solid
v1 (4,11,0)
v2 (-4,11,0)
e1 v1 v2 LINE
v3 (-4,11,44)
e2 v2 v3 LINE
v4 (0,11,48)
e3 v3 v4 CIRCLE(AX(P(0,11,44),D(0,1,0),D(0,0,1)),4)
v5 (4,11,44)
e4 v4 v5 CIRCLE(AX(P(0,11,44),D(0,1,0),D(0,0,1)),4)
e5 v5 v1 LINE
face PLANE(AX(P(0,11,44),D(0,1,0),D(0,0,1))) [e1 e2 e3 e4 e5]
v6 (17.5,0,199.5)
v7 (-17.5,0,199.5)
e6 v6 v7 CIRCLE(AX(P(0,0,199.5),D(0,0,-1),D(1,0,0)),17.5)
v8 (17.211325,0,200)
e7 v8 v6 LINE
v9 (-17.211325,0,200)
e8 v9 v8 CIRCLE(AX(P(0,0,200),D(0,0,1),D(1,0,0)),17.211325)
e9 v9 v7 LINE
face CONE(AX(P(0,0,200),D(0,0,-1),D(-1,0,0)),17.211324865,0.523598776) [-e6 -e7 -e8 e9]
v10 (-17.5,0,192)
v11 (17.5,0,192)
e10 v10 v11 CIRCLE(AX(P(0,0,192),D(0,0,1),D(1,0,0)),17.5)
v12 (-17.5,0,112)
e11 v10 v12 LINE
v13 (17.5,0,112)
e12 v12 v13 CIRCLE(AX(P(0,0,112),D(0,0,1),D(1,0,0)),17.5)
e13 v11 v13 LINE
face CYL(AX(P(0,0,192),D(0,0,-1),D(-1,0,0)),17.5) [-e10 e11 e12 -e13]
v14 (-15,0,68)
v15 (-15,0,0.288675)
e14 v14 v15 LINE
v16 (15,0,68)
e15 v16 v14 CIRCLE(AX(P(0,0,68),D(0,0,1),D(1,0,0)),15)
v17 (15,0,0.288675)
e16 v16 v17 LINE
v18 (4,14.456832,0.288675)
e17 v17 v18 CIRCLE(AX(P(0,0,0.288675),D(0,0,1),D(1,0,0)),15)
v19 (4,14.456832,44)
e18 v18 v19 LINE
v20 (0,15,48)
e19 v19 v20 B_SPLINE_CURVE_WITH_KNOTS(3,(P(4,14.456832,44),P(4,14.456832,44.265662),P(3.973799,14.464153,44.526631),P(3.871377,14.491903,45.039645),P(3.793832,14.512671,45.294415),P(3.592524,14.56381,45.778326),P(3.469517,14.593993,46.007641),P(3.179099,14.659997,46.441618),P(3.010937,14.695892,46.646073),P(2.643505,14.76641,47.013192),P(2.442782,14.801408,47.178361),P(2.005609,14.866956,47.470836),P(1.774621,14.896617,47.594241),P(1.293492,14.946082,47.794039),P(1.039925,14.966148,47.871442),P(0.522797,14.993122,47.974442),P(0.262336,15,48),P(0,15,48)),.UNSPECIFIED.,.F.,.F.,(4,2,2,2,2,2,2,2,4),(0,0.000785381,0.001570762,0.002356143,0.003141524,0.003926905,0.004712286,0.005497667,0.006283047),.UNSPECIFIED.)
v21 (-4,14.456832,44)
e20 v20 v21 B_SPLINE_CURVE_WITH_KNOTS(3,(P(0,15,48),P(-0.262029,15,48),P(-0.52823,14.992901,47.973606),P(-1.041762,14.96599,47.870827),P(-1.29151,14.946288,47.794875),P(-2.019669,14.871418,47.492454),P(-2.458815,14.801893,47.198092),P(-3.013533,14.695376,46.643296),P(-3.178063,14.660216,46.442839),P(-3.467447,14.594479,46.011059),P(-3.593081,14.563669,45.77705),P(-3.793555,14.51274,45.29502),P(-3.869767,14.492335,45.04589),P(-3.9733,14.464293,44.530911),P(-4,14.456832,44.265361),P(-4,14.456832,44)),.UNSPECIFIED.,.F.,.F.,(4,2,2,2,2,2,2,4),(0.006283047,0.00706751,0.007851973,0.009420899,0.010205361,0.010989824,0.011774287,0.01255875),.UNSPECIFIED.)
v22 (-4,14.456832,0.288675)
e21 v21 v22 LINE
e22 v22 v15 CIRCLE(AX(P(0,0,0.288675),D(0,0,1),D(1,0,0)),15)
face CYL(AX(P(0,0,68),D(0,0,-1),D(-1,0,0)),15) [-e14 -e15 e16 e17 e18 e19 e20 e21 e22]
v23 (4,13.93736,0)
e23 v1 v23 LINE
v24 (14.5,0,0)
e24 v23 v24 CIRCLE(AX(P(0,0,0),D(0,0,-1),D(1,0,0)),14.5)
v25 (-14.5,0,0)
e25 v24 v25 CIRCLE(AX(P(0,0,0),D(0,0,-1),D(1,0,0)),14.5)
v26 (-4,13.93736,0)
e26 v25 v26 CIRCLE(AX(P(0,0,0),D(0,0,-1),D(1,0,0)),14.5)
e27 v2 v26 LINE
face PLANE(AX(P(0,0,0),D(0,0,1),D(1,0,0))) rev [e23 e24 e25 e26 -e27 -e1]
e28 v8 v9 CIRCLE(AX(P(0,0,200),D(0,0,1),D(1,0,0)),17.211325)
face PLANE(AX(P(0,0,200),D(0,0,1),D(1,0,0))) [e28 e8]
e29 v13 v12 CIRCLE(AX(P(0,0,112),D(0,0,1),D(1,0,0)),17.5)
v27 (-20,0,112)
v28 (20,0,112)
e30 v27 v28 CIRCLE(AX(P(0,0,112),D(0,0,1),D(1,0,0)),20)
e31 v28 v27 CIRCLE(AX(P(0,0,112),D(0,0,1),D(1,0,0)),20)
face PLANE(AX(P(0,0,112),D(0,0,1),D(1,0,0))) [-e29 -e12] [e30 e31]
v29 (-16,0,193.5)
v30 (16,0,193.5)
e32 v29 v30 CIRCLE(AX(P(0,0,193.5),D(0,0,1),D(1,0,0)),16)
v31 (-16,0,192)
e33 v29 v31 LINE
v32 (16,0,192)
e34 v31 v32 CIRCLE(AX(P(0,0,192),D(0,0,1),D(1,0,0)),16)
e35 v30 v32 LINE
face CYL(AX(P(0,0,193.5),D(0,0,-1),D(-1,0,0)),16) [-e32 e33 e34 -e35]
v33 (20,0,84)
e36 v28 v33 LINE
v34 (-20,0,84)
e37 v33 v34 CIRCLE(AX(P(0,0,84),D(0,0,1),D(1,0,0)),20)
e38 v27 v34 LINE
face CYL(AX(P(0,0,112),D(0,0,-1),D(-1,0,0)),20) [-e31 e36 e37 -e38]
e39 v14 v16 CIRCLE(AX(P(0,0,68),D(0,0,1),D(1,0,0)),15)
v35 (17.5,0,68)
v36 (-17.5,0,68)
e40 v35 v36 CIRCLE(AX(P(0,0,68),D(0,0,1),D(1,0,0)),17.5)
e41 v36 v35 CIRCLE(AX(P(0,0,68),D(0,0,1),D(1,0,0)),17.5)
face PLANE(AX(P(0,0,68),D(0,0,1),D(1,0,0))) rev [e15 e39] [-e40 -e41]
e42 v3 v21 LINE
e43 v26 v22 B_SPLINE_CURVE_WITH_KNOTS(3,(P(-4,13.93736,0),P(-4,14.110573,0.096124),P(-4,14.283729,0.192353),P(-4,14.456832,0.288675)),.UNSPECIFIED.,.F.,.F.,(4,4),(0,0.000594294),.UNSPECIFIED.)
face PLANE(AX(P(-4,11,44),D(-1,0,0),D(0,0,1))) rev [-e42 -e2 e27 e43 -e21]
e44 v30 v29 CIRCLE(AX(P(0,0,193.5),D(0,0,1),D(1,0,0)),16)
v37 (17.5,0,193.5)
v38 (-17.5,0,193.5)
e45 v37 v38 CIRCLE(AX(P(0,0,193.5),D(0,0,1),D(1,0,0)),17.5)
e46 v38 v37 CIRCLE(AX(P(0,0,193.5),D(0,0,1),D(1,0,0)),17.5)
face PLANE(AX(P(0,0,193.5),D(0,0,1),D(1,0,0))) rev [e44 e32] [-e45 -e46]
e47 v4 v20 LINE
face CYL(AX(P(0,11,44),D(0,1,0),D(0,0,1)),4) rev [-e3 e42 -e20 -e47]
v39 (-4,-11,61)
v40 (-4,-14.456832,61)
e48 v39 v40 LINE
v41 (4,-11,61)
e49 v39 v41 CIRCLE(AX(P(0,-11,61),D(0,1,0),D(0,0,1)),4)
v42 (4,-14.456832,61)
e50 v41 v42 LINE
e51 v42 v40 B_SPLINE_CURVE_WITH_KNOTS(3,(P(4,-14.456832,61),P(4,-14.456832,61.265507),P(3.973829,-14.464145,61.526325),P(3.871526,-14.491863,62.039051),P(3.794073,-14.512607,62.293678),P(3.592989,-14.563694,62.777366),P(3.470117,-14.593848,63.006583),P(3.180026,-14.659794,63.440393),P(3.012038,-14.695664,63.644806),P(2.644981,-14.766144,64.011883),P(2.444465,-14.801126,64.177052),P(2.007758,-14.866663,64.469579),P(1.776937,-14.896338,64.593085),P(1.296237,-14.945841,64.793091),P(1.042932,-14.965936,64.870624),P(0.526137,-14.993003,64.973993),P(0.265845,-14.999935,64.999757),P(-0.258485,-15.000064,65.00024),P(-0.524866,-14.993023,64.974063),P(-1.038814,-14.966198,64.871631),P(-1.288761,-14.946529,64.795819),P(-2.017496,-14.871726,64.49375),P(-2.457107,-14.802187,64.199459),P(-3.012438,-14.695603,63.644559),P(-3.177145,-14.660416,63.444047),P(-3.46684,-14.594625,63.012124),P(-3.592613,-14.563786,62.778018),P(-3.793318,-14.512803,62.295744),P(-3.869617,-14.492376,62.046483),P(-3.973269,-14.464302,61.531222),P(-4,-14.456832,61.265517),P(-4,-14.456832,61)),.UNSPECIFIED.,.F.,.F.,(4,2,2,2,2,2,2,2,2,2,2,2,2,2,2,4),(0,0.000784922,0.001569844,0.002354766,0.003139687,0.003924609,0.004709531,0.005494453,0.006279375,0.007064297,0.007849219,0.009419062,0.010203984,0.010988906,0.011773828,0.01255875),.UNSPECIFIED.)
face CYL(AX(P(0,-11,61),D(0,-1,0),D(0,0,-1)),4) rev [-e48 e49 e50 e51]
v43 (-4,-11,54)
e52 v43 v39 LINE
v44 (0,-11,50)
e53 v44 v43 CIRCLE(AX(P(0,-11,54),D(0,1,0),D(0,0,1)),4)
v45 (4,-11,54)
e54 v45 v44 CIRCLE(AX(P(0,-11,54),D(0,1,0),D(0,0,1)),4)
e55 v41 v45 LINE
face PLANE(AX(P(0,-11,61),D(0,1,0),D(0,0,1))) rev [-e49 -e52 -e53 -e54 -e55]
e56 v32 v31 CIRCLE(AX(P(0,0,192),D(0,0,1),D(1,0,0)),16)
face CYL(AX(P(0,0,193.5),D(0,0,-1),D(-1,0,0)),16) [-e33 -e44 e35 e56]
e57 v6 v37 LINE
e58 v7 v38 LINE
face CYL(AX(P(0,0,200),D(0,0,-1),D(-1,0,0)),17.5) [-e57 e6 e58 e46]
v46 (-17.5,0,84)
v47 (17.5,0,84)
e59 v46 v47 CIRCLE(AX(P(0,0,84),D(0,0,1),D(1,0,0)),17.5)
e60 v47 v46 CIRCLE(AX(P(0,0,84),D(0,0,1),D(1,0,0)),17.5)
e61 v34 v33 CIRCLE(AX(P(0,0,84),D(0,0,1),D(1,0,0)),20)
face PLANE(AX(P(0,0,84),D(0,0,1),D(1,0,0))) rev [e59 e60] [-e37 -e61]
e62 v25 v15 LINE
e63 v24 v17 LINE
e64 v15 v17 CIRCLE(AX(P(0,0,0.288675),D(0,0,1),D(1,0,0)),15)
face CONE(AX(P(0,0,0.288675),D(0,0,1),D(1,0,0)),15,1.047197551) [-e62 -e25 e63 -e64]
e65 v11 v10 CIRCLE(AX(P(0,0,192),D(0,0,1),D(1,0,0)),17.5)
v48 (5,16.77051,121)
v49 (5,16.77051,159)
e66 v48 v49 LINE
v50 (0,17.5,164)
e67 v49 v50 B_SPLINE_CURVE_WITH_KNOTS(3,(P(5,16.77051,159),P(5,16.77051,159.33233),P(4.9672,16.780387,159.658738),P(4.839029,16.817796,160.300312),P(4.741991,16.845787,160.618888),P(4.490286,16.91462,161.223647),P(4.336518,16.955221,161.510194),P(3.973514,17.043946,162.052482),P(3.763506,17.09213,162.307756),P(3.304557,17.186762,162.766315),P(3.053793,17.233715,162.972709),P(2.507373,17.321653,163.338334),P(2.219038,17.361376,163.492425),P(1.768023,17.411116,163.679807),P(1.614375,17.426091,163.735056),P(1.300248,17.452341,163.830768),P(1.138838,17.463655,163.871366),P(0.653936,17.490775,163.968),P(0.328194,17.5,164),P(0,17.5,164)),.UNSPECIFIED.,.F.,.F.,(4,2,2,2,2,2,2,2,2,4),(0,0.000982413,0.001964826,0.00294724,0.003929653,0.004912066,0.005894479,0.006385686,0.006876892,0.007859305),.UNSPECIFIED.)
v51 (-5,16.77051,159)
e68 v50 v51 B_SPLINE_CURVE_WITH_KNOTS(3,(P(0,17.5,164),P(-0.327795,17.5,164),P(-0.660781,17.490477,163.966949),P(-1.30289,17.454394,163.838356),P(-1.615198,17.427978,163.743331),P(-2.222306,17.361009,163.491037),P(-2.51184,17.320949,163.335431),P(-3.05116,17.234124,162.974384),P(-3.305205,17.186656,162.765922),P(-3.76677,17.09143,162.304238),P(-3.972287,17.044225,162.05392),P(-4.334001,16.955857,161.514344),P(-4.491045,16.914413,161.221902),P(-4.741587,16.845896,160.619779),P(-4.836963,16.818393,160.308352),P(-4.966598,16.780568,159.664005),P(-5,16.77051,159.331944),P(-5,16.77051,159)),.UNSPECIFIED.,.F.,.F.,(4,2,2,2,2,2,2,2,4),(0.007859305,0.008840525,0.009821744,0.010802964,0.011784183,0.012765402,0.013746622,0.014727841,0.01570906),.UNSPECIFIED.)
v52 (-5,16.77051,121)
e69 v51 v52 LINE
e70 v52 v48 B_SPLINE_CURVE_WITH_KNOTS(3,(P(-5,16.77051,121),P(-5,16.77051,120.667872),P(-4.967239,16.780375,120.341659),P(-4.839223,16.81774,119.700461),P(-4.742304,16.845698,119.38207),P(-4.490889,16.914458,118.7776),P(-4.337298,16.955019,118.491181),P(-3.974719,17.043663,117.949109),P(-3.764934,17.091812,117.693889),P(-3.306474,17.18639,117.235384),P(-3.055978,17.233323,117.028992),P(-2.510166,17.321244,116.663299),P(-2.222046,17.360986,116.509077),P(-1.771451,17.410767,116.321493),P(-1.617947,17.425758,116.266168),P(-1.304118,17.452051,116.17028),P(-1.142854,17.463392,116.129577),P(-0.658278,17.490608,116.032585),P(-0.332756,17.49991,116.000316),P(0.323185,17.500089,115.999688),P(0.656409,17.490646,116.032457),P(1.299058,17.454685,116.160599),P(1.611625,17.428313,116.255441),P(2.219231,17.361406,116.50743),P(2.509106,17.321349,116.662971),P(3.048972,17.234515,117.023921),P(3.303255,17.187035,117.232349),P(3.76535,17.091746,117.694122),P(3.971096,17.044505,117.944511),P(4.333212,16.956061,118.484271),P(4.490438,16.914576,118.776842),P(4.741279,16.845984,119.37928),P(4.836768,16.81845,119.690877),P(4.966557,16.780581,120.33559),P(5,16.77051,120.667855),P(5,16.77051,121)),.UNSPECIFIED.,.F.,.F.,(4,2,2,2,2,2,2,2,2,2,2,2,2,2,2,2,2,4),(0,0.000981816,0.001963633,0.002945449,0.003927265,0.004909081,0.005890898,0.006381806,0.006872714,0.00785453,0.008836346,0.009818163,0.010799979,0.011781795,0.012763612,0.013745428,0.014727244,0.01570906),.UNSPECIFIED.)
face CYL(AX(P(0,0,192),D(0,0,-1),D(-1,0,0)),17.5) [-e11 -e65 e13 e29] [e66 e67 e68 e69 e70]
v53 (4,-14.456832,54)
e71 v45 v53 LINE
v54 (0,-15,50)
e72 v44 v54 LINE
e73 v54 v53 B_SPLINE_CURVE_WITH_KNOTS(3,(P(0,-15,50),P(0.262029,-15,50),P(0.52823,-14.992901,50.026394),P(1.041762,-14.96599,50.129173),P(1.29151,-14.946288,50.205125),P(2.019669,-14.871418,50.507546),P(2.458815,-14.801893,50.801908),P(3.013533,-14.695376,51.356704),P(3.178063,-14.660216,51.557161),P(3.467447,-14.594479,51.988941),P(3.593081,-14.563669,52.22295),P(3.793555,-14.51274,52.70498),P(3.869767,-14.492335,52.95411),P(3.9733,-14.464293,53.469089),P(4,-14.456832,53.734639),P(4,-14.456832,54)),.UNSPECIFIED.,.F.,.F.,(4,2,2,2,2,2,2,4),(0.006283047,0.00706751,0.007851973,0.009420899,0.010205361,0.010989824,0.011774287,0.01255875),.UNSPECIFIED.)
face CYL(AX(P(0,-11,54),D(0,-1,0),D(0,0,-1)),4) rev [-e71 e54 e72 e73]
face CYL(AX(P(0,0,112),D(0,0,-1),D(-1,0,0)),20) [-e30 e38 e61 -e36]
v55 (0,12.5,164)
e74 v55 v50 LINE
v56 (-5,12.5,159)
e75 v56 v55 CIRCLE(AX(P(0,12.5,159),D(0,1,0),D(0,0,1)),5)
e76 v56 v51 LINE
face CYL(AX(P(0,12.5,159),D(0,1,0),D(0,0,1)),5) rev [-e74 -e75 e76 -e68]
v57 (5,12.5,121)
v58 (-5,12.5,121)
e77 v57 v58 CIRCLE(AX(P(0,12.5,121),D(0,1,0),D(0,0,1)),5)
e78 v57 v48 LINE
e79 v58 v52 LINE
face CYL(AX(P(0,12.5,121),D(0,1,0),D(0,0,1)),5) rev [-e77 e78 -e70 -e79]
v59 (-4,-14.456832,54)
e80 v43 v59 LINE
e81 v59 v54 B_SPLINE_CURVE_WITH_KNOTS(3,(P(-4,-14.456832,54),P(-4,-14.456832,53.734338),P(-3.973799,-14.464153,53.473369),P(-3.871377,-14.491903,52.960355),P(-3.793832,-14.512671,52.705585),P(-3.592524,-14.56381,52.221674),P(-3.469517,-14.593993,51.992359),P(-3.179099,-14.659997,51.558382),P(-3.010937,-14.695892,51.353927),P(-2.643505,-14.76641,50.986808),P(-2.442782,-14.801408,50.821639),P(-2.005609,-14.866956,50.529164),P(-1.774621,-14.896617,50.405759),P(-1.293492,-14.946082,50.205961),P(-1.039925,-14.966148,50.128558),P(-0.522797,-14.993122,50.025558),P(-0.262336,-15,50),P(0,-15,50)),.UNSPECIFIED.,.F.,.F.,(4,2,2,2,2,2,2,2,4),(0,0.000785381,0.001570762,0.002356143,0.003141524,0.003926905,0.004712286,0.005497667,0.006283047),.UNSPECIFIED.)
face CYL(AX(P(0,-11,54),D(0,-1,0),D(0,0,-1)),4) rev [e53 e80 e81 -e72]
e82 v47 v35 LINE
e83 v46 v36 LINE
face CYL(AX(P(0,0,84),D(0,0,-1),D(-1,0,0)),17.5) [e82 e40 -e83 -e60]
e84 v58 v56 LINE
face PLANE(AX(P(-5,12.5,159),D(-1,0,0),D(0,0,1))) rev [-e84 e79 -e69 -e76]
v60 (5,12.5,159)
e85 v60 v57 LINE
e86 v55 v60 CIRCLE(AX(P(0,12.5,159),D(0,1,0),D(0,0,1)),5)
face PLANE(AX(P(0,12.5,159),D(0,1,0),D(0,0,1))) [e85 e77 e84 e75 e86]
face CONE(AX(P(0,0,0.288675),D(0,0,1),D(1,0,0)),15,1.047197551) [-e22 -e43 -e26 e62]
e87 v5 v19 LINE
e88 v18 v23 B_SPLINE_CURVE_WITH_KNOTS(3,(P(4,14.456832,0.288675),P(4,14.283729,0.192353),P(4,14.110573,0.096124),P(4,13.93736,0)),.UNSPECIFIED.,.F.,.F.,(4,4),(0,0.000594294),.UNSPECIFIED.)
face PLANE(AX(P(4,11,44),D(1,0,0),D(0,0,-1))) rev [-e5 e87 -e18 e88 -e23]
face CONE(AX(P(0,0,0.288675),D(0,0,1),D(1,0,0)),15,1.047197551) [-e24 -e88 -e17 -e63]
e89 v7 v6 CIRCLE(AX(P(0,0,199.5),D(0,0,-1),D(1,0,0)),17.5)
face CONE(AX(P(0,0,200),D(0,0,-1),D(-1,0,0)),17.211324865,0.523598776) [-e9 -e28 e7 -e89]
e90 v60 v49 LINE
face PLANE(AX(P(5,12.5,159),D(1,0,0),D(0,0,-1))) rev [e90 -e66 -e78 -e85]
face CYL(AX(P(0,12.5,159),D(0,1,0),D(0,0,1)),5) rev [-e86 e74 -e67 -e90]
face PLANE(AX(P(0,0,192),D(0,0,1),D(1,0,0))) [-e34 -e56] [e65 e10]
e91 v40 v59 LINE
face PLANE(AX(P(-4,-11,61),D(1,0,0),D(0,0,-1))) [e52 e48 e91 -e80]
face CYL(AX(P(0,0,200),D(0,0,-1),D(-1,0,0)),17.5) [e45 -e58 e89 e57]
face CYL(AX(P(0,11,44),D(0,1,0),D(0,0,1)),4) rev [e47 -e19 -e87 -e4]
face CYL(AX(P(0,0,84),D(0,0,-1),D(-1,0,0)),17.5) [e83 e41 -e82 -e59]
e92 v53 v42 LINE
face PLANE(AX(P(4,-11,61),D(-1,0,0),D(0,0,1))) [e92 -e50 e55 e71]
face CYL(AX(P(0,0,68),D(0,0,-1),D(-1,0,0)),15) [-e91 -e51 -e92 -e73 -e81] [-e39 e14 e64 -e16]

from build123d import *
from OCP.BRepFilletAPI import BRepFilletAPI_MakeChamfer

# Parameters (mm, degrees)
SKETCH1_R           = 15
BOSS_EXTRUDE1_DEPTH = 68
SKETCH2_R           = 17.5
BOSS_EXTRUDE2_DEPTH = 16
SKETCH3_R           = 20
BOSS_EXTRUDE3_DEPTH = 28
SKETCH4_R           = 17.5
BOSS_EXTRUDE4_DEPTH = 80
SKETCH5_R           = 16
BOSS_EXTRUDE5_DEPTH = 1.5
SKETCH6_R           = 17.5
BOSS_EXTRUDE6_DEPTH = 6.5
CUT_EXTRUDE1_START  = 17.5
CUT_EXTRUDE1_DEPTH  = 5
CUT_EXTRUDE2_START  = 15
CUT_EXTRUDE2_DEPTH  = 4
CUT_EXTRUDE3_START  = -15
CUT_EXTRUDE3_DEPTH  = 4
CHAMFER1_SIZE       = 0.5
CHAMFER1_SIZE2      = 0.288675135


with BuildPart() as part:
    # Sketch1 → Boss-Extrude1 (new body)
    with BuildSketch(Plane.XY):
        Circle(SKETCH1_R)
    extrude(amount=BOSS_EXTRUDE1_DEPTH)

    # Sketch2 → Boss-Extrude2 (add)
    with BuildSketch(Plane.XY.offset(68)):
        Circle(SKETCH2_R)
    extrude(amount=BOSS_EXTRUDE2_DEPTH)

    # Sketch3 → Boss-Extrude3 (add)
    with BuildSketch(Plane.XY.offset(84)):
        Circle(SKETCH3_R)
    extrude(amount=BOSS_EXTRUDE3_DEPTH)

    # Sketch4 → Boss-Extrude4 (add)
    with BuildSketch(Plane.XY.offset(112)):
        Circle(SKETCH4_R)
    extrude(amount=BOSS_EXTRUDE4_DEPTH)

    # Sketch5 → Boss-Extrude5 (add)
    with BuildSketch(Plane.XY.offset(192)):
        Circle(SKETCH5_R)
    extrude(amount=BOSS_EXTRUDE5_DEPTH)

    # Sketch6 → Boss-Extrude6 (add)
    with BuildSketch(Plane.XY.offset(193.5)):
        Circle(SKETCH6_R)
    extrude(amount=BOSS_EXTRUDE6_DEPTH)

    # Sketch7 → Cut-Extrude1 (cut)
    with BuildSketch(Plane(origin=(0, 0, 0), x_dir=(1, 0, 0), z_dir=(0, 1, 0)).offset(CUT_EXTRUDE1_START)):
        with BuildLine():
            Line((-5, -159), (-5, -121))
            ThreePointArc((-5, -121), (0, -116), (5, -121))
            Line((5, -121), (5, -159))
            ThreePointArc((5, -159), (0, -164), (-5, -159))
        make_face()
    extrude(amount=-CUT_EXTRUDE1_DEPTH, mode=Mode.SUBTRACT)

    # Sketch8 → Cut-Extrude2 (cut)
    with BuildSketch(Plane(origin=(0, 0, 0), x_dir=(1, 0, 0), z_dir=(0, 1, 0)).offset(CUT_EXTRUDE2_START)):
        with BuildLine():
            Line((-4, -44), (-4, 0))
            ThreePointArc((-4, 0), (0, 4), (4, 0))
            Line((4, 0), (4, -44))
            ThreePointArc((4, -44), (0, -48), (-4, -44))
        make_face()
    extrude(amount=-CUT_EXTRUDE2_DEPTH, mode=Mode.SUBTRACT)

    # Sketch9 → Cut-Extrude3 (cut)
    with BuildSketch(Plane(origin=(0, 0, 0), x_dir=(1, 0, 0), z_dir=(0, 1, 0)).offset(CUT_EXTRUDE3_START)):
        with BuildLine():
            Line((-4, -61), (-4, -54))
            ThreePointArc((-4, -54), (0, -50), (4, -54))
            Line((4, -54), (4, -61))
            ThreePointArc((4, -61), (0, -65), (-4, -61))
        make_face()
    extrude(amount=CUT_EXTRUDE3_DEPTH, mode=Mode.SUBTRACT)

    # Chamfer1: one chamfer whose edges measure the first distance from different faces: ONE call of the kernel's chamfer builder (chamfer() names one face for all edges)
    chamfer1_edges_1 = [part.edges().sort_by_distance(p)[0] for p in [
        (-17.5, 0, 200),
    ]]
    chamfer1_side_1 = [part.faces().sort_by_distance(p)[0] for p in [
        (-17.5, 0, 196.75),
    ]]
    chamfer1_edges_2 = [part.edges().sort_by_distance(p)[0] for p in [
        (-9.082951062, -11.937336386, 0),
    ]]
    chamfer1_side_2 = [part.faces().sort_by_distance(p)[0] for p in [
        (0, -0.583570782, 0),
    ]]
    chamfer1 = BRepFilletAPI_MakeChamfer(part.part.solid().wrapped)
    for e in chamfer1_edges_1:
        chamfer1.Add(CHAMFER1_SIZE, CHAMFER1_SIZE2, e.wrapped, chamfer1_side_1[0].wrapped)  # the first distance lies on this face
    for e in chamfer1_edges_2:
        chamfer1.Add(CHAMFER1_SIZE, CHAMFER1_SIZE2, e.wrapped, chamfer1_side_2[0].wrapped)  # the first distance lies on this face
    add(Compound.cast(chamfer1.Shape()), mode=Mode.REPLACE)


solid = part.part
